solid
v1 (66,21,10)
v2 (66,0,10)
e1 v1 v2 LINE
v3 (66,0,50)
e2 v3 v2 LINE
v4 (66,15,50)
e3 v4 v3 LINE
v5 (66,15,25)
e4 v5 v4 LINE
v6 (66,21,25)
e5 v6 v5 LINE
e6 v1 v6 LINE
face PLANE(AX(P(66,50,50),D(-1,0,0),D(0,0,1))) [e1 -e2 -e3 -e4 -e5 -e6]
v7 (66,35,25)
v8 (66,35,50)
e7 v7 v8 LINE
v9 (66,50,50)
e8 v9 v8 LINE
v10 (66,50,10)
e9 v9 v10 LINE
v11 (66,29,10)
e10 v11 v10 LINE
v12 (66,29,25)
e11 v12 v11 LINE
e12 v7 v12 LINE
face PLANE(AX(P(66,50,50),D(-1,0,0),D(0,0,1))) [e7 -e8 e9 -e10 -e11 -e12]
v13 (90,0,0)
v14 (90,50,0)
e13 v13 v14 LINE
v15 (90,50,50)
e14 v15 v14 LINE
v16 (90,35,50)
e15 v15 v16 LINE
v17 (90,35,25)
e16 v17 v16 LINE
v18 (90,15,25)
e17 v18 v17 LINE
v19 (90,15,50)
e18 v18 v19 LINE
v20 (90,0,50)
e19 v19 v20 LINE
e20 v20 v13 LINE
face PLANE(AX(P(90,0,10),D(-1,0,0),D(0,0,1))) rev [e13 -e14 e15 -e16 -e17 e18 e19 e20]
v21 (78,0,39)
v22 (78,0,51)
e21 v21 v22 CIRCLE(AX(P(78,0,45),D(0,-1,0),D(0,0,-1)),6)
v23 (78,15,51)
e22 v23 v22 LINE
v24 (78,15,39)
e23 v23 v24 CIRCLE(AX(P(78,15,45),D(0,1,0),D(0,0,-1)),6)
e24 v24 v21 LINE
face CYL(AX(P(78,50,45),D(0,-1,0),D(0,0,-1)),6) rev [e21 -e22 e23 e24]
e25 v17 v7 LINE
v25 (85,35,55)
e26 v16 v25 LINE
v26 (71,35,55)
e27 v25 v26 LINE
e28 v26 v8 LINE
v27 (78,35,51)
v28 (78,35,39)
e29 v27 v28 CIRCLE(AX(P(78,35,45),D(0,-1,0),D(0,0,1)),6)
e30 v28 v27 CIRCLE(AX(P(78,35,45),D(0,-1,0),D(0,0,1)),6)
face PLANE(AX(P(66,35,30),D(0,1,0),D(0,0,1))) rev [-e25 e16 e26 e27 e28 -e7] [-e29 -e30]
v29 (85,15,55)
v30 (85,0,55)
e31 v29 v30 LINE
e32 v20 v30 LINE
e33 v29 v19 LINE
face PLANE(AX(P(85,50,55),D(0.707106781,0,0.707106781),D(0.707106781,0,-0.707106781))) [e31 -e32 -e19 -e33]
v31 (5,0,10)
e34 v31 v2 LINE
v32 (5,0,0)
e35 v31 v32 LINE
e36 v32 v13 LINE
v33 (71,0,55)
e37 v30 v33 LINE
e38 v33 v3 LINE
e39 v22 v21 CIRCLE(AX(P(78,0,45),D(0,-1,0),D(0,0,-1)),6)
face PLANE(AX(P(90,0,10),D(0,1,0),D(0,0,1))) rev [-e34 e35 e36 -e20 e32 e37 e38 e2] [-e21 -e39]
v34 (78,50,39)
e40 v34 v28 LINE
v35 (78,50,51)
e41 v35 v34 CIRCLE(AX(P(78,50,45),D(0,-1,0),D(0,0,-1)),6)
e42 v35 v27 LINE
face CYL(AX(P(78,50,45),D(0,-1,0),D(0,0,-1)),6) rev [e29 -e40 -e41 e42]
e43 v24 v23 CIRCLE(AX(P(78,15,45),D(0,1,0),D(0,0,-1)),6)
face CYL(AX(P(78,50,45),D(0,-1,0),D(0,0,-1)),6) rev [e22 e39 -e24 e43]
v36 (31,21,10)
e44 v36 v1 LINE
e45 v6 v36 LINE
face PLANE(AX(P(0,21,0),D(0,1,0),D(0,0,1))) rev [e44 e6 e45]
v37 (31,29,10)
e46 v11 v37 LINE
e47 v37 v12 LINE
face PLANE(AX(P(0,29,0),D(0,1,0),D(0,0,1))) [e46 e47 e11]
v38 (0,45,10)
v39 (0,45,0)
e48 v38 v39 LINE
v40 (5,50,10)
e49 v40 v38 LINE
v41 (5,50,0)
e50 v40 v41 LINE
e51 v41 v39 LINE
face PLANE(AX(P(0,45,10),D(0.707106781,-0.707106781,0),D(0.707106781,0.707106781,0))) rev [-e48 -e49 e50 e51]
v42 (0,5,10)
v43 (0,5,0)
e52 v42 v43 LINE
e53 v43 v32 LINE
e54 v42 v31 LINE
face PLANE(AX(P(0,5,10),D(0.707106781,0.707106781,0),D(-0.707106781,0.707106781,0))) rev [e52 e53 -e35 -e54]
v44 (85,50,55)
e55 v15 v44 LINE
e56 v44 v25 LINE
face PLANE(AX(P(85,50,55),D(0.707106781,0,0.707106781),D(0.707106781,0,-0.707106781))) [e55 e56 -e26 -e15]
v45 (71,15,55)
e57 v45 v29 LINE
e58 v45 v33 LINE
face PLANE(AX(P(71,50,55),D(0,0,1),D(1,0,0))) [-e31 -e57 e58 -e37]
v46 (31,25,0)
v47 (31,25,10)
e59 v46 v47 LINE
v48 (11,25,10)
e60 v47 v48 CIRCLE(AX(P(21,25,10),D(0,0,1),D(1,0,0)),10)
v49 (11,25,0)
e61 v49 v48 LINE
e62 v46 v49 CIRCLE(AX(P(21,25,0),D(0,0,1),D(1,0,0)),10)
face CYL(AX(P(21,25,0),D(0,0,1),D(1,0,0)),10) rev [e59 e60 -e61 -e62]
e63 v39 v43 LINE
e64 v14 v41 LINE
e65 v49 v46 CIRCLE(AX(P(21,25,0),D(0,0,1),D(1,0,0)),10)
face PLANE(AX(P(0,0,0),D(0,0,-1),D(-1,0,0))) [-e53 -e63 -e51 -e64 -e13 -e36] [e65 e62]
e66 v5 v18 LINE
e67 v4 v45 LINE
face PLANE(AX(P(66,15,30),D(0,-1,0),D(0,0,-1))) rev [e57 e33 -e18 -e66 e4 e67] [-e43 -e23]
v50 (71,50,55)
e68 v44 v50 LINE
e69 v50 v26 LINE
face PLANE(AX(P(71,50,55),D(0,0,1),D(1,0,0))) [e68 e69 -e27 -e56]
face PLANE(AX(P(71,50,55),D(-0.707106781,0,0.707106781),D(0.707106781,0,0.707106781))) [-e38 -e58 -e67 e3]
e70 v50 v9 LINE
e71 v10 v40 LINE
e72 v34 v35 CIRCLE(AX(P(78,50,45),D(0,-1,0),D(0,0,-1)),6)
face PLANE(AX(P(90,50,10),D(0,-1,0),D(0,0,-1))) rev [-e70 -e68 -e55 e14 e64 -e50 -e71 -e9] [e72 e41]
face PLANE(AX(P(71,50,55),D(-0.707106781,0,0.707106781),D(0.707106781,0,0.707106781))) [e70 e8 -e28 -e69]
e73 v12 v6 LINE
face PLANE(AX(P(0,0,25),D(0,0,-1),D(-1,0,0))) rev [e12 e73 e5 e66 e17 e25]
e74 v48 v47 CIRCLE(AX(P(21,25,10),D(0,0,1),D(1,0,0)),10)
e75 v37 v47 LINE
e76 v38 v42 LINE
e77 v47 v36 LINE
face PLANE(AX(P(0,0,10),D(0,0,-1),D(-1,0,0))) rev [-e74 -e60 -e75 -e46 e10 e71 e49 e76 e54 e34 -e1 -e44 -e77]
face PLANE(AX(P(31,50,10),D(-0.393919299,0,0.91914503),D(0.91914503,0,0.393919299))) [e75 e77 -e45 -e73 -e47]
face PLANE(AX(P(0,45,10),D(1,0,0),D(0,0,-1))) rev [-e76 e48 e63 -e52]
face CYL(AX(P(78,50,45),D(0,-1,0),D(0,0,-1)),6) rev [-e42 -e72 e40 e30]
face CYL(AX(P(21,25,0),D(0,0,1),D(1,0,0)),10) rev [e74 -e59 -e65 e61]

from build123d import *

# Parameters (mm, degrees)
BASE_PLATE_DEPTH            = 10
UPRIGHT_WALL_DEPTH          = 50
CLEVIS_PIN_HOLE_SKETCH_R    = 6
CLEVIS_PIN_HOLE_DEPTH       = 50
CLEVIS_SLOT_SKETCH_W        = 24
CLEVIS_SLOT_SKETCH_H        = 20
CLEVIS_SLOT_DEPTH           = 25
PLATE_BORE_SKETCH_R         = 10
PLATE_BORE_DEPTH            = 10
GUSSET_RIB_DEPTH            = 50
RIB_TRIM_CUT_1_DEPTH        = 21
RIB_TRIM_CUT_2_DEPTH        = 21
SLOT_RELIEF_POCKET_SKETCH_W = 24
SLOT_RELIEF_POCKET_SKETCH_H = 20
SLOT_RELIEF_POCKET_DEPTH    = 5


with BuildPart() as part:
    # Base Plate Profile → Base Plate (new body)
    with BuildSketch(Plane.XY):
        Polygon((90, 0), (5, 0), (0, 5), (0, 45), (5, 50), (90, 50), align=None)
    extrude(amount=BASE_PLATE_DEPTH)

    # Upright Wall Profile → Upright Wall (add)
    with BuildSketch(Plane.XZ):
        Polygon((90, 10), (90, 50), (85, 55), (71, 55), (66, 50), (66, 10), align=None)
    extrude(amount=-UPRIGHT_WALL_DEPTH)

    # Clevis Pin Hole Sketch → Clevis Pin Hole (cut)
    with BuildSketch(Plane.XZ):
        with Locations(Location((78, 45, 0), (0, 0, 270))):
            Circle(CLEVIS_PIN_HOLE_SKETCH_R)
    extrude(amount=-CLEVIS_PIN_HOLE_DEPTH, mode=Mode.SUBTRACT)

    # Clevis Slot Sketch → Clevis Slot (cut)
    with BuildSketch(Plane.XY.offset(55)):
        with Locations((78, 25)):
            Rectangle(CLEVIS_SLOT_SKETCH_W, CLEVIS_SLOT_SKETCH_H)
    extrude(amount=-CLEVIS_SLOT_DEPTH, mode=Mode.SUBTRACT)

    # Plate Bore Sketch → Plate Bore (cut)
    with BuildSketch(Plane.XY.offset(10)):
        with Locations((21, 25)):
            Circle(PLATE_BORE_SKETCH_R)
    extrude(amount=-PLATE_BORE_DEPTH, mode=Mode.SUBTRACT)

    # Gusset Rib Profile → Gusset Rib (add)
    with BuildSketch(Plane.XZ):
        Polygon((66, 10), (66, 25), (31, 10), align=None)
    extrude(amount=-GUSSET_RIB_DEPTH)

    # Rib Trim Cut 1 Sketch → Rib Trim Cut 1 (cut)
    with BuildSketch(Plane.XZ):
        Polygon((66, 25), (66, 10), (31, 10), align=None)
    extrude(amount=-RIB_TRIM_CUT_1_DEPTH, mode=Mode.SUBTRACT)

    # Rib Trim Cut 2 Sketch → Rib Trim Cut 2 (cut)
    with BuildSketch(Plane(origin=(0, 50, 0), x_dir=(1, 0, 0), z_dir=(0, 1, 0))):
        Polygon((66, -25), (66, -10), (31, -10), align=None)
    extrude(amount=-RIB_TRIM_CUT_2_DEPTH, mode=Mode.SUBTRACT)

    # Slot Relief Pocket Sketch → Slot Relief Pocket (cut)
    with BuildSketch(Plane.XY.offset(30)):
        with Locations((78, 25)):
            Rectangle(SLOT_RELIEF_POCKET_SKETCH_W, SLOT_RELIEF_POCKET_SKETCH_H)
    extrude(amount=-SLOT_RELIEF_POCKET_DEPTH, mode=Mode.SUBTRACT)


solid = part.part
